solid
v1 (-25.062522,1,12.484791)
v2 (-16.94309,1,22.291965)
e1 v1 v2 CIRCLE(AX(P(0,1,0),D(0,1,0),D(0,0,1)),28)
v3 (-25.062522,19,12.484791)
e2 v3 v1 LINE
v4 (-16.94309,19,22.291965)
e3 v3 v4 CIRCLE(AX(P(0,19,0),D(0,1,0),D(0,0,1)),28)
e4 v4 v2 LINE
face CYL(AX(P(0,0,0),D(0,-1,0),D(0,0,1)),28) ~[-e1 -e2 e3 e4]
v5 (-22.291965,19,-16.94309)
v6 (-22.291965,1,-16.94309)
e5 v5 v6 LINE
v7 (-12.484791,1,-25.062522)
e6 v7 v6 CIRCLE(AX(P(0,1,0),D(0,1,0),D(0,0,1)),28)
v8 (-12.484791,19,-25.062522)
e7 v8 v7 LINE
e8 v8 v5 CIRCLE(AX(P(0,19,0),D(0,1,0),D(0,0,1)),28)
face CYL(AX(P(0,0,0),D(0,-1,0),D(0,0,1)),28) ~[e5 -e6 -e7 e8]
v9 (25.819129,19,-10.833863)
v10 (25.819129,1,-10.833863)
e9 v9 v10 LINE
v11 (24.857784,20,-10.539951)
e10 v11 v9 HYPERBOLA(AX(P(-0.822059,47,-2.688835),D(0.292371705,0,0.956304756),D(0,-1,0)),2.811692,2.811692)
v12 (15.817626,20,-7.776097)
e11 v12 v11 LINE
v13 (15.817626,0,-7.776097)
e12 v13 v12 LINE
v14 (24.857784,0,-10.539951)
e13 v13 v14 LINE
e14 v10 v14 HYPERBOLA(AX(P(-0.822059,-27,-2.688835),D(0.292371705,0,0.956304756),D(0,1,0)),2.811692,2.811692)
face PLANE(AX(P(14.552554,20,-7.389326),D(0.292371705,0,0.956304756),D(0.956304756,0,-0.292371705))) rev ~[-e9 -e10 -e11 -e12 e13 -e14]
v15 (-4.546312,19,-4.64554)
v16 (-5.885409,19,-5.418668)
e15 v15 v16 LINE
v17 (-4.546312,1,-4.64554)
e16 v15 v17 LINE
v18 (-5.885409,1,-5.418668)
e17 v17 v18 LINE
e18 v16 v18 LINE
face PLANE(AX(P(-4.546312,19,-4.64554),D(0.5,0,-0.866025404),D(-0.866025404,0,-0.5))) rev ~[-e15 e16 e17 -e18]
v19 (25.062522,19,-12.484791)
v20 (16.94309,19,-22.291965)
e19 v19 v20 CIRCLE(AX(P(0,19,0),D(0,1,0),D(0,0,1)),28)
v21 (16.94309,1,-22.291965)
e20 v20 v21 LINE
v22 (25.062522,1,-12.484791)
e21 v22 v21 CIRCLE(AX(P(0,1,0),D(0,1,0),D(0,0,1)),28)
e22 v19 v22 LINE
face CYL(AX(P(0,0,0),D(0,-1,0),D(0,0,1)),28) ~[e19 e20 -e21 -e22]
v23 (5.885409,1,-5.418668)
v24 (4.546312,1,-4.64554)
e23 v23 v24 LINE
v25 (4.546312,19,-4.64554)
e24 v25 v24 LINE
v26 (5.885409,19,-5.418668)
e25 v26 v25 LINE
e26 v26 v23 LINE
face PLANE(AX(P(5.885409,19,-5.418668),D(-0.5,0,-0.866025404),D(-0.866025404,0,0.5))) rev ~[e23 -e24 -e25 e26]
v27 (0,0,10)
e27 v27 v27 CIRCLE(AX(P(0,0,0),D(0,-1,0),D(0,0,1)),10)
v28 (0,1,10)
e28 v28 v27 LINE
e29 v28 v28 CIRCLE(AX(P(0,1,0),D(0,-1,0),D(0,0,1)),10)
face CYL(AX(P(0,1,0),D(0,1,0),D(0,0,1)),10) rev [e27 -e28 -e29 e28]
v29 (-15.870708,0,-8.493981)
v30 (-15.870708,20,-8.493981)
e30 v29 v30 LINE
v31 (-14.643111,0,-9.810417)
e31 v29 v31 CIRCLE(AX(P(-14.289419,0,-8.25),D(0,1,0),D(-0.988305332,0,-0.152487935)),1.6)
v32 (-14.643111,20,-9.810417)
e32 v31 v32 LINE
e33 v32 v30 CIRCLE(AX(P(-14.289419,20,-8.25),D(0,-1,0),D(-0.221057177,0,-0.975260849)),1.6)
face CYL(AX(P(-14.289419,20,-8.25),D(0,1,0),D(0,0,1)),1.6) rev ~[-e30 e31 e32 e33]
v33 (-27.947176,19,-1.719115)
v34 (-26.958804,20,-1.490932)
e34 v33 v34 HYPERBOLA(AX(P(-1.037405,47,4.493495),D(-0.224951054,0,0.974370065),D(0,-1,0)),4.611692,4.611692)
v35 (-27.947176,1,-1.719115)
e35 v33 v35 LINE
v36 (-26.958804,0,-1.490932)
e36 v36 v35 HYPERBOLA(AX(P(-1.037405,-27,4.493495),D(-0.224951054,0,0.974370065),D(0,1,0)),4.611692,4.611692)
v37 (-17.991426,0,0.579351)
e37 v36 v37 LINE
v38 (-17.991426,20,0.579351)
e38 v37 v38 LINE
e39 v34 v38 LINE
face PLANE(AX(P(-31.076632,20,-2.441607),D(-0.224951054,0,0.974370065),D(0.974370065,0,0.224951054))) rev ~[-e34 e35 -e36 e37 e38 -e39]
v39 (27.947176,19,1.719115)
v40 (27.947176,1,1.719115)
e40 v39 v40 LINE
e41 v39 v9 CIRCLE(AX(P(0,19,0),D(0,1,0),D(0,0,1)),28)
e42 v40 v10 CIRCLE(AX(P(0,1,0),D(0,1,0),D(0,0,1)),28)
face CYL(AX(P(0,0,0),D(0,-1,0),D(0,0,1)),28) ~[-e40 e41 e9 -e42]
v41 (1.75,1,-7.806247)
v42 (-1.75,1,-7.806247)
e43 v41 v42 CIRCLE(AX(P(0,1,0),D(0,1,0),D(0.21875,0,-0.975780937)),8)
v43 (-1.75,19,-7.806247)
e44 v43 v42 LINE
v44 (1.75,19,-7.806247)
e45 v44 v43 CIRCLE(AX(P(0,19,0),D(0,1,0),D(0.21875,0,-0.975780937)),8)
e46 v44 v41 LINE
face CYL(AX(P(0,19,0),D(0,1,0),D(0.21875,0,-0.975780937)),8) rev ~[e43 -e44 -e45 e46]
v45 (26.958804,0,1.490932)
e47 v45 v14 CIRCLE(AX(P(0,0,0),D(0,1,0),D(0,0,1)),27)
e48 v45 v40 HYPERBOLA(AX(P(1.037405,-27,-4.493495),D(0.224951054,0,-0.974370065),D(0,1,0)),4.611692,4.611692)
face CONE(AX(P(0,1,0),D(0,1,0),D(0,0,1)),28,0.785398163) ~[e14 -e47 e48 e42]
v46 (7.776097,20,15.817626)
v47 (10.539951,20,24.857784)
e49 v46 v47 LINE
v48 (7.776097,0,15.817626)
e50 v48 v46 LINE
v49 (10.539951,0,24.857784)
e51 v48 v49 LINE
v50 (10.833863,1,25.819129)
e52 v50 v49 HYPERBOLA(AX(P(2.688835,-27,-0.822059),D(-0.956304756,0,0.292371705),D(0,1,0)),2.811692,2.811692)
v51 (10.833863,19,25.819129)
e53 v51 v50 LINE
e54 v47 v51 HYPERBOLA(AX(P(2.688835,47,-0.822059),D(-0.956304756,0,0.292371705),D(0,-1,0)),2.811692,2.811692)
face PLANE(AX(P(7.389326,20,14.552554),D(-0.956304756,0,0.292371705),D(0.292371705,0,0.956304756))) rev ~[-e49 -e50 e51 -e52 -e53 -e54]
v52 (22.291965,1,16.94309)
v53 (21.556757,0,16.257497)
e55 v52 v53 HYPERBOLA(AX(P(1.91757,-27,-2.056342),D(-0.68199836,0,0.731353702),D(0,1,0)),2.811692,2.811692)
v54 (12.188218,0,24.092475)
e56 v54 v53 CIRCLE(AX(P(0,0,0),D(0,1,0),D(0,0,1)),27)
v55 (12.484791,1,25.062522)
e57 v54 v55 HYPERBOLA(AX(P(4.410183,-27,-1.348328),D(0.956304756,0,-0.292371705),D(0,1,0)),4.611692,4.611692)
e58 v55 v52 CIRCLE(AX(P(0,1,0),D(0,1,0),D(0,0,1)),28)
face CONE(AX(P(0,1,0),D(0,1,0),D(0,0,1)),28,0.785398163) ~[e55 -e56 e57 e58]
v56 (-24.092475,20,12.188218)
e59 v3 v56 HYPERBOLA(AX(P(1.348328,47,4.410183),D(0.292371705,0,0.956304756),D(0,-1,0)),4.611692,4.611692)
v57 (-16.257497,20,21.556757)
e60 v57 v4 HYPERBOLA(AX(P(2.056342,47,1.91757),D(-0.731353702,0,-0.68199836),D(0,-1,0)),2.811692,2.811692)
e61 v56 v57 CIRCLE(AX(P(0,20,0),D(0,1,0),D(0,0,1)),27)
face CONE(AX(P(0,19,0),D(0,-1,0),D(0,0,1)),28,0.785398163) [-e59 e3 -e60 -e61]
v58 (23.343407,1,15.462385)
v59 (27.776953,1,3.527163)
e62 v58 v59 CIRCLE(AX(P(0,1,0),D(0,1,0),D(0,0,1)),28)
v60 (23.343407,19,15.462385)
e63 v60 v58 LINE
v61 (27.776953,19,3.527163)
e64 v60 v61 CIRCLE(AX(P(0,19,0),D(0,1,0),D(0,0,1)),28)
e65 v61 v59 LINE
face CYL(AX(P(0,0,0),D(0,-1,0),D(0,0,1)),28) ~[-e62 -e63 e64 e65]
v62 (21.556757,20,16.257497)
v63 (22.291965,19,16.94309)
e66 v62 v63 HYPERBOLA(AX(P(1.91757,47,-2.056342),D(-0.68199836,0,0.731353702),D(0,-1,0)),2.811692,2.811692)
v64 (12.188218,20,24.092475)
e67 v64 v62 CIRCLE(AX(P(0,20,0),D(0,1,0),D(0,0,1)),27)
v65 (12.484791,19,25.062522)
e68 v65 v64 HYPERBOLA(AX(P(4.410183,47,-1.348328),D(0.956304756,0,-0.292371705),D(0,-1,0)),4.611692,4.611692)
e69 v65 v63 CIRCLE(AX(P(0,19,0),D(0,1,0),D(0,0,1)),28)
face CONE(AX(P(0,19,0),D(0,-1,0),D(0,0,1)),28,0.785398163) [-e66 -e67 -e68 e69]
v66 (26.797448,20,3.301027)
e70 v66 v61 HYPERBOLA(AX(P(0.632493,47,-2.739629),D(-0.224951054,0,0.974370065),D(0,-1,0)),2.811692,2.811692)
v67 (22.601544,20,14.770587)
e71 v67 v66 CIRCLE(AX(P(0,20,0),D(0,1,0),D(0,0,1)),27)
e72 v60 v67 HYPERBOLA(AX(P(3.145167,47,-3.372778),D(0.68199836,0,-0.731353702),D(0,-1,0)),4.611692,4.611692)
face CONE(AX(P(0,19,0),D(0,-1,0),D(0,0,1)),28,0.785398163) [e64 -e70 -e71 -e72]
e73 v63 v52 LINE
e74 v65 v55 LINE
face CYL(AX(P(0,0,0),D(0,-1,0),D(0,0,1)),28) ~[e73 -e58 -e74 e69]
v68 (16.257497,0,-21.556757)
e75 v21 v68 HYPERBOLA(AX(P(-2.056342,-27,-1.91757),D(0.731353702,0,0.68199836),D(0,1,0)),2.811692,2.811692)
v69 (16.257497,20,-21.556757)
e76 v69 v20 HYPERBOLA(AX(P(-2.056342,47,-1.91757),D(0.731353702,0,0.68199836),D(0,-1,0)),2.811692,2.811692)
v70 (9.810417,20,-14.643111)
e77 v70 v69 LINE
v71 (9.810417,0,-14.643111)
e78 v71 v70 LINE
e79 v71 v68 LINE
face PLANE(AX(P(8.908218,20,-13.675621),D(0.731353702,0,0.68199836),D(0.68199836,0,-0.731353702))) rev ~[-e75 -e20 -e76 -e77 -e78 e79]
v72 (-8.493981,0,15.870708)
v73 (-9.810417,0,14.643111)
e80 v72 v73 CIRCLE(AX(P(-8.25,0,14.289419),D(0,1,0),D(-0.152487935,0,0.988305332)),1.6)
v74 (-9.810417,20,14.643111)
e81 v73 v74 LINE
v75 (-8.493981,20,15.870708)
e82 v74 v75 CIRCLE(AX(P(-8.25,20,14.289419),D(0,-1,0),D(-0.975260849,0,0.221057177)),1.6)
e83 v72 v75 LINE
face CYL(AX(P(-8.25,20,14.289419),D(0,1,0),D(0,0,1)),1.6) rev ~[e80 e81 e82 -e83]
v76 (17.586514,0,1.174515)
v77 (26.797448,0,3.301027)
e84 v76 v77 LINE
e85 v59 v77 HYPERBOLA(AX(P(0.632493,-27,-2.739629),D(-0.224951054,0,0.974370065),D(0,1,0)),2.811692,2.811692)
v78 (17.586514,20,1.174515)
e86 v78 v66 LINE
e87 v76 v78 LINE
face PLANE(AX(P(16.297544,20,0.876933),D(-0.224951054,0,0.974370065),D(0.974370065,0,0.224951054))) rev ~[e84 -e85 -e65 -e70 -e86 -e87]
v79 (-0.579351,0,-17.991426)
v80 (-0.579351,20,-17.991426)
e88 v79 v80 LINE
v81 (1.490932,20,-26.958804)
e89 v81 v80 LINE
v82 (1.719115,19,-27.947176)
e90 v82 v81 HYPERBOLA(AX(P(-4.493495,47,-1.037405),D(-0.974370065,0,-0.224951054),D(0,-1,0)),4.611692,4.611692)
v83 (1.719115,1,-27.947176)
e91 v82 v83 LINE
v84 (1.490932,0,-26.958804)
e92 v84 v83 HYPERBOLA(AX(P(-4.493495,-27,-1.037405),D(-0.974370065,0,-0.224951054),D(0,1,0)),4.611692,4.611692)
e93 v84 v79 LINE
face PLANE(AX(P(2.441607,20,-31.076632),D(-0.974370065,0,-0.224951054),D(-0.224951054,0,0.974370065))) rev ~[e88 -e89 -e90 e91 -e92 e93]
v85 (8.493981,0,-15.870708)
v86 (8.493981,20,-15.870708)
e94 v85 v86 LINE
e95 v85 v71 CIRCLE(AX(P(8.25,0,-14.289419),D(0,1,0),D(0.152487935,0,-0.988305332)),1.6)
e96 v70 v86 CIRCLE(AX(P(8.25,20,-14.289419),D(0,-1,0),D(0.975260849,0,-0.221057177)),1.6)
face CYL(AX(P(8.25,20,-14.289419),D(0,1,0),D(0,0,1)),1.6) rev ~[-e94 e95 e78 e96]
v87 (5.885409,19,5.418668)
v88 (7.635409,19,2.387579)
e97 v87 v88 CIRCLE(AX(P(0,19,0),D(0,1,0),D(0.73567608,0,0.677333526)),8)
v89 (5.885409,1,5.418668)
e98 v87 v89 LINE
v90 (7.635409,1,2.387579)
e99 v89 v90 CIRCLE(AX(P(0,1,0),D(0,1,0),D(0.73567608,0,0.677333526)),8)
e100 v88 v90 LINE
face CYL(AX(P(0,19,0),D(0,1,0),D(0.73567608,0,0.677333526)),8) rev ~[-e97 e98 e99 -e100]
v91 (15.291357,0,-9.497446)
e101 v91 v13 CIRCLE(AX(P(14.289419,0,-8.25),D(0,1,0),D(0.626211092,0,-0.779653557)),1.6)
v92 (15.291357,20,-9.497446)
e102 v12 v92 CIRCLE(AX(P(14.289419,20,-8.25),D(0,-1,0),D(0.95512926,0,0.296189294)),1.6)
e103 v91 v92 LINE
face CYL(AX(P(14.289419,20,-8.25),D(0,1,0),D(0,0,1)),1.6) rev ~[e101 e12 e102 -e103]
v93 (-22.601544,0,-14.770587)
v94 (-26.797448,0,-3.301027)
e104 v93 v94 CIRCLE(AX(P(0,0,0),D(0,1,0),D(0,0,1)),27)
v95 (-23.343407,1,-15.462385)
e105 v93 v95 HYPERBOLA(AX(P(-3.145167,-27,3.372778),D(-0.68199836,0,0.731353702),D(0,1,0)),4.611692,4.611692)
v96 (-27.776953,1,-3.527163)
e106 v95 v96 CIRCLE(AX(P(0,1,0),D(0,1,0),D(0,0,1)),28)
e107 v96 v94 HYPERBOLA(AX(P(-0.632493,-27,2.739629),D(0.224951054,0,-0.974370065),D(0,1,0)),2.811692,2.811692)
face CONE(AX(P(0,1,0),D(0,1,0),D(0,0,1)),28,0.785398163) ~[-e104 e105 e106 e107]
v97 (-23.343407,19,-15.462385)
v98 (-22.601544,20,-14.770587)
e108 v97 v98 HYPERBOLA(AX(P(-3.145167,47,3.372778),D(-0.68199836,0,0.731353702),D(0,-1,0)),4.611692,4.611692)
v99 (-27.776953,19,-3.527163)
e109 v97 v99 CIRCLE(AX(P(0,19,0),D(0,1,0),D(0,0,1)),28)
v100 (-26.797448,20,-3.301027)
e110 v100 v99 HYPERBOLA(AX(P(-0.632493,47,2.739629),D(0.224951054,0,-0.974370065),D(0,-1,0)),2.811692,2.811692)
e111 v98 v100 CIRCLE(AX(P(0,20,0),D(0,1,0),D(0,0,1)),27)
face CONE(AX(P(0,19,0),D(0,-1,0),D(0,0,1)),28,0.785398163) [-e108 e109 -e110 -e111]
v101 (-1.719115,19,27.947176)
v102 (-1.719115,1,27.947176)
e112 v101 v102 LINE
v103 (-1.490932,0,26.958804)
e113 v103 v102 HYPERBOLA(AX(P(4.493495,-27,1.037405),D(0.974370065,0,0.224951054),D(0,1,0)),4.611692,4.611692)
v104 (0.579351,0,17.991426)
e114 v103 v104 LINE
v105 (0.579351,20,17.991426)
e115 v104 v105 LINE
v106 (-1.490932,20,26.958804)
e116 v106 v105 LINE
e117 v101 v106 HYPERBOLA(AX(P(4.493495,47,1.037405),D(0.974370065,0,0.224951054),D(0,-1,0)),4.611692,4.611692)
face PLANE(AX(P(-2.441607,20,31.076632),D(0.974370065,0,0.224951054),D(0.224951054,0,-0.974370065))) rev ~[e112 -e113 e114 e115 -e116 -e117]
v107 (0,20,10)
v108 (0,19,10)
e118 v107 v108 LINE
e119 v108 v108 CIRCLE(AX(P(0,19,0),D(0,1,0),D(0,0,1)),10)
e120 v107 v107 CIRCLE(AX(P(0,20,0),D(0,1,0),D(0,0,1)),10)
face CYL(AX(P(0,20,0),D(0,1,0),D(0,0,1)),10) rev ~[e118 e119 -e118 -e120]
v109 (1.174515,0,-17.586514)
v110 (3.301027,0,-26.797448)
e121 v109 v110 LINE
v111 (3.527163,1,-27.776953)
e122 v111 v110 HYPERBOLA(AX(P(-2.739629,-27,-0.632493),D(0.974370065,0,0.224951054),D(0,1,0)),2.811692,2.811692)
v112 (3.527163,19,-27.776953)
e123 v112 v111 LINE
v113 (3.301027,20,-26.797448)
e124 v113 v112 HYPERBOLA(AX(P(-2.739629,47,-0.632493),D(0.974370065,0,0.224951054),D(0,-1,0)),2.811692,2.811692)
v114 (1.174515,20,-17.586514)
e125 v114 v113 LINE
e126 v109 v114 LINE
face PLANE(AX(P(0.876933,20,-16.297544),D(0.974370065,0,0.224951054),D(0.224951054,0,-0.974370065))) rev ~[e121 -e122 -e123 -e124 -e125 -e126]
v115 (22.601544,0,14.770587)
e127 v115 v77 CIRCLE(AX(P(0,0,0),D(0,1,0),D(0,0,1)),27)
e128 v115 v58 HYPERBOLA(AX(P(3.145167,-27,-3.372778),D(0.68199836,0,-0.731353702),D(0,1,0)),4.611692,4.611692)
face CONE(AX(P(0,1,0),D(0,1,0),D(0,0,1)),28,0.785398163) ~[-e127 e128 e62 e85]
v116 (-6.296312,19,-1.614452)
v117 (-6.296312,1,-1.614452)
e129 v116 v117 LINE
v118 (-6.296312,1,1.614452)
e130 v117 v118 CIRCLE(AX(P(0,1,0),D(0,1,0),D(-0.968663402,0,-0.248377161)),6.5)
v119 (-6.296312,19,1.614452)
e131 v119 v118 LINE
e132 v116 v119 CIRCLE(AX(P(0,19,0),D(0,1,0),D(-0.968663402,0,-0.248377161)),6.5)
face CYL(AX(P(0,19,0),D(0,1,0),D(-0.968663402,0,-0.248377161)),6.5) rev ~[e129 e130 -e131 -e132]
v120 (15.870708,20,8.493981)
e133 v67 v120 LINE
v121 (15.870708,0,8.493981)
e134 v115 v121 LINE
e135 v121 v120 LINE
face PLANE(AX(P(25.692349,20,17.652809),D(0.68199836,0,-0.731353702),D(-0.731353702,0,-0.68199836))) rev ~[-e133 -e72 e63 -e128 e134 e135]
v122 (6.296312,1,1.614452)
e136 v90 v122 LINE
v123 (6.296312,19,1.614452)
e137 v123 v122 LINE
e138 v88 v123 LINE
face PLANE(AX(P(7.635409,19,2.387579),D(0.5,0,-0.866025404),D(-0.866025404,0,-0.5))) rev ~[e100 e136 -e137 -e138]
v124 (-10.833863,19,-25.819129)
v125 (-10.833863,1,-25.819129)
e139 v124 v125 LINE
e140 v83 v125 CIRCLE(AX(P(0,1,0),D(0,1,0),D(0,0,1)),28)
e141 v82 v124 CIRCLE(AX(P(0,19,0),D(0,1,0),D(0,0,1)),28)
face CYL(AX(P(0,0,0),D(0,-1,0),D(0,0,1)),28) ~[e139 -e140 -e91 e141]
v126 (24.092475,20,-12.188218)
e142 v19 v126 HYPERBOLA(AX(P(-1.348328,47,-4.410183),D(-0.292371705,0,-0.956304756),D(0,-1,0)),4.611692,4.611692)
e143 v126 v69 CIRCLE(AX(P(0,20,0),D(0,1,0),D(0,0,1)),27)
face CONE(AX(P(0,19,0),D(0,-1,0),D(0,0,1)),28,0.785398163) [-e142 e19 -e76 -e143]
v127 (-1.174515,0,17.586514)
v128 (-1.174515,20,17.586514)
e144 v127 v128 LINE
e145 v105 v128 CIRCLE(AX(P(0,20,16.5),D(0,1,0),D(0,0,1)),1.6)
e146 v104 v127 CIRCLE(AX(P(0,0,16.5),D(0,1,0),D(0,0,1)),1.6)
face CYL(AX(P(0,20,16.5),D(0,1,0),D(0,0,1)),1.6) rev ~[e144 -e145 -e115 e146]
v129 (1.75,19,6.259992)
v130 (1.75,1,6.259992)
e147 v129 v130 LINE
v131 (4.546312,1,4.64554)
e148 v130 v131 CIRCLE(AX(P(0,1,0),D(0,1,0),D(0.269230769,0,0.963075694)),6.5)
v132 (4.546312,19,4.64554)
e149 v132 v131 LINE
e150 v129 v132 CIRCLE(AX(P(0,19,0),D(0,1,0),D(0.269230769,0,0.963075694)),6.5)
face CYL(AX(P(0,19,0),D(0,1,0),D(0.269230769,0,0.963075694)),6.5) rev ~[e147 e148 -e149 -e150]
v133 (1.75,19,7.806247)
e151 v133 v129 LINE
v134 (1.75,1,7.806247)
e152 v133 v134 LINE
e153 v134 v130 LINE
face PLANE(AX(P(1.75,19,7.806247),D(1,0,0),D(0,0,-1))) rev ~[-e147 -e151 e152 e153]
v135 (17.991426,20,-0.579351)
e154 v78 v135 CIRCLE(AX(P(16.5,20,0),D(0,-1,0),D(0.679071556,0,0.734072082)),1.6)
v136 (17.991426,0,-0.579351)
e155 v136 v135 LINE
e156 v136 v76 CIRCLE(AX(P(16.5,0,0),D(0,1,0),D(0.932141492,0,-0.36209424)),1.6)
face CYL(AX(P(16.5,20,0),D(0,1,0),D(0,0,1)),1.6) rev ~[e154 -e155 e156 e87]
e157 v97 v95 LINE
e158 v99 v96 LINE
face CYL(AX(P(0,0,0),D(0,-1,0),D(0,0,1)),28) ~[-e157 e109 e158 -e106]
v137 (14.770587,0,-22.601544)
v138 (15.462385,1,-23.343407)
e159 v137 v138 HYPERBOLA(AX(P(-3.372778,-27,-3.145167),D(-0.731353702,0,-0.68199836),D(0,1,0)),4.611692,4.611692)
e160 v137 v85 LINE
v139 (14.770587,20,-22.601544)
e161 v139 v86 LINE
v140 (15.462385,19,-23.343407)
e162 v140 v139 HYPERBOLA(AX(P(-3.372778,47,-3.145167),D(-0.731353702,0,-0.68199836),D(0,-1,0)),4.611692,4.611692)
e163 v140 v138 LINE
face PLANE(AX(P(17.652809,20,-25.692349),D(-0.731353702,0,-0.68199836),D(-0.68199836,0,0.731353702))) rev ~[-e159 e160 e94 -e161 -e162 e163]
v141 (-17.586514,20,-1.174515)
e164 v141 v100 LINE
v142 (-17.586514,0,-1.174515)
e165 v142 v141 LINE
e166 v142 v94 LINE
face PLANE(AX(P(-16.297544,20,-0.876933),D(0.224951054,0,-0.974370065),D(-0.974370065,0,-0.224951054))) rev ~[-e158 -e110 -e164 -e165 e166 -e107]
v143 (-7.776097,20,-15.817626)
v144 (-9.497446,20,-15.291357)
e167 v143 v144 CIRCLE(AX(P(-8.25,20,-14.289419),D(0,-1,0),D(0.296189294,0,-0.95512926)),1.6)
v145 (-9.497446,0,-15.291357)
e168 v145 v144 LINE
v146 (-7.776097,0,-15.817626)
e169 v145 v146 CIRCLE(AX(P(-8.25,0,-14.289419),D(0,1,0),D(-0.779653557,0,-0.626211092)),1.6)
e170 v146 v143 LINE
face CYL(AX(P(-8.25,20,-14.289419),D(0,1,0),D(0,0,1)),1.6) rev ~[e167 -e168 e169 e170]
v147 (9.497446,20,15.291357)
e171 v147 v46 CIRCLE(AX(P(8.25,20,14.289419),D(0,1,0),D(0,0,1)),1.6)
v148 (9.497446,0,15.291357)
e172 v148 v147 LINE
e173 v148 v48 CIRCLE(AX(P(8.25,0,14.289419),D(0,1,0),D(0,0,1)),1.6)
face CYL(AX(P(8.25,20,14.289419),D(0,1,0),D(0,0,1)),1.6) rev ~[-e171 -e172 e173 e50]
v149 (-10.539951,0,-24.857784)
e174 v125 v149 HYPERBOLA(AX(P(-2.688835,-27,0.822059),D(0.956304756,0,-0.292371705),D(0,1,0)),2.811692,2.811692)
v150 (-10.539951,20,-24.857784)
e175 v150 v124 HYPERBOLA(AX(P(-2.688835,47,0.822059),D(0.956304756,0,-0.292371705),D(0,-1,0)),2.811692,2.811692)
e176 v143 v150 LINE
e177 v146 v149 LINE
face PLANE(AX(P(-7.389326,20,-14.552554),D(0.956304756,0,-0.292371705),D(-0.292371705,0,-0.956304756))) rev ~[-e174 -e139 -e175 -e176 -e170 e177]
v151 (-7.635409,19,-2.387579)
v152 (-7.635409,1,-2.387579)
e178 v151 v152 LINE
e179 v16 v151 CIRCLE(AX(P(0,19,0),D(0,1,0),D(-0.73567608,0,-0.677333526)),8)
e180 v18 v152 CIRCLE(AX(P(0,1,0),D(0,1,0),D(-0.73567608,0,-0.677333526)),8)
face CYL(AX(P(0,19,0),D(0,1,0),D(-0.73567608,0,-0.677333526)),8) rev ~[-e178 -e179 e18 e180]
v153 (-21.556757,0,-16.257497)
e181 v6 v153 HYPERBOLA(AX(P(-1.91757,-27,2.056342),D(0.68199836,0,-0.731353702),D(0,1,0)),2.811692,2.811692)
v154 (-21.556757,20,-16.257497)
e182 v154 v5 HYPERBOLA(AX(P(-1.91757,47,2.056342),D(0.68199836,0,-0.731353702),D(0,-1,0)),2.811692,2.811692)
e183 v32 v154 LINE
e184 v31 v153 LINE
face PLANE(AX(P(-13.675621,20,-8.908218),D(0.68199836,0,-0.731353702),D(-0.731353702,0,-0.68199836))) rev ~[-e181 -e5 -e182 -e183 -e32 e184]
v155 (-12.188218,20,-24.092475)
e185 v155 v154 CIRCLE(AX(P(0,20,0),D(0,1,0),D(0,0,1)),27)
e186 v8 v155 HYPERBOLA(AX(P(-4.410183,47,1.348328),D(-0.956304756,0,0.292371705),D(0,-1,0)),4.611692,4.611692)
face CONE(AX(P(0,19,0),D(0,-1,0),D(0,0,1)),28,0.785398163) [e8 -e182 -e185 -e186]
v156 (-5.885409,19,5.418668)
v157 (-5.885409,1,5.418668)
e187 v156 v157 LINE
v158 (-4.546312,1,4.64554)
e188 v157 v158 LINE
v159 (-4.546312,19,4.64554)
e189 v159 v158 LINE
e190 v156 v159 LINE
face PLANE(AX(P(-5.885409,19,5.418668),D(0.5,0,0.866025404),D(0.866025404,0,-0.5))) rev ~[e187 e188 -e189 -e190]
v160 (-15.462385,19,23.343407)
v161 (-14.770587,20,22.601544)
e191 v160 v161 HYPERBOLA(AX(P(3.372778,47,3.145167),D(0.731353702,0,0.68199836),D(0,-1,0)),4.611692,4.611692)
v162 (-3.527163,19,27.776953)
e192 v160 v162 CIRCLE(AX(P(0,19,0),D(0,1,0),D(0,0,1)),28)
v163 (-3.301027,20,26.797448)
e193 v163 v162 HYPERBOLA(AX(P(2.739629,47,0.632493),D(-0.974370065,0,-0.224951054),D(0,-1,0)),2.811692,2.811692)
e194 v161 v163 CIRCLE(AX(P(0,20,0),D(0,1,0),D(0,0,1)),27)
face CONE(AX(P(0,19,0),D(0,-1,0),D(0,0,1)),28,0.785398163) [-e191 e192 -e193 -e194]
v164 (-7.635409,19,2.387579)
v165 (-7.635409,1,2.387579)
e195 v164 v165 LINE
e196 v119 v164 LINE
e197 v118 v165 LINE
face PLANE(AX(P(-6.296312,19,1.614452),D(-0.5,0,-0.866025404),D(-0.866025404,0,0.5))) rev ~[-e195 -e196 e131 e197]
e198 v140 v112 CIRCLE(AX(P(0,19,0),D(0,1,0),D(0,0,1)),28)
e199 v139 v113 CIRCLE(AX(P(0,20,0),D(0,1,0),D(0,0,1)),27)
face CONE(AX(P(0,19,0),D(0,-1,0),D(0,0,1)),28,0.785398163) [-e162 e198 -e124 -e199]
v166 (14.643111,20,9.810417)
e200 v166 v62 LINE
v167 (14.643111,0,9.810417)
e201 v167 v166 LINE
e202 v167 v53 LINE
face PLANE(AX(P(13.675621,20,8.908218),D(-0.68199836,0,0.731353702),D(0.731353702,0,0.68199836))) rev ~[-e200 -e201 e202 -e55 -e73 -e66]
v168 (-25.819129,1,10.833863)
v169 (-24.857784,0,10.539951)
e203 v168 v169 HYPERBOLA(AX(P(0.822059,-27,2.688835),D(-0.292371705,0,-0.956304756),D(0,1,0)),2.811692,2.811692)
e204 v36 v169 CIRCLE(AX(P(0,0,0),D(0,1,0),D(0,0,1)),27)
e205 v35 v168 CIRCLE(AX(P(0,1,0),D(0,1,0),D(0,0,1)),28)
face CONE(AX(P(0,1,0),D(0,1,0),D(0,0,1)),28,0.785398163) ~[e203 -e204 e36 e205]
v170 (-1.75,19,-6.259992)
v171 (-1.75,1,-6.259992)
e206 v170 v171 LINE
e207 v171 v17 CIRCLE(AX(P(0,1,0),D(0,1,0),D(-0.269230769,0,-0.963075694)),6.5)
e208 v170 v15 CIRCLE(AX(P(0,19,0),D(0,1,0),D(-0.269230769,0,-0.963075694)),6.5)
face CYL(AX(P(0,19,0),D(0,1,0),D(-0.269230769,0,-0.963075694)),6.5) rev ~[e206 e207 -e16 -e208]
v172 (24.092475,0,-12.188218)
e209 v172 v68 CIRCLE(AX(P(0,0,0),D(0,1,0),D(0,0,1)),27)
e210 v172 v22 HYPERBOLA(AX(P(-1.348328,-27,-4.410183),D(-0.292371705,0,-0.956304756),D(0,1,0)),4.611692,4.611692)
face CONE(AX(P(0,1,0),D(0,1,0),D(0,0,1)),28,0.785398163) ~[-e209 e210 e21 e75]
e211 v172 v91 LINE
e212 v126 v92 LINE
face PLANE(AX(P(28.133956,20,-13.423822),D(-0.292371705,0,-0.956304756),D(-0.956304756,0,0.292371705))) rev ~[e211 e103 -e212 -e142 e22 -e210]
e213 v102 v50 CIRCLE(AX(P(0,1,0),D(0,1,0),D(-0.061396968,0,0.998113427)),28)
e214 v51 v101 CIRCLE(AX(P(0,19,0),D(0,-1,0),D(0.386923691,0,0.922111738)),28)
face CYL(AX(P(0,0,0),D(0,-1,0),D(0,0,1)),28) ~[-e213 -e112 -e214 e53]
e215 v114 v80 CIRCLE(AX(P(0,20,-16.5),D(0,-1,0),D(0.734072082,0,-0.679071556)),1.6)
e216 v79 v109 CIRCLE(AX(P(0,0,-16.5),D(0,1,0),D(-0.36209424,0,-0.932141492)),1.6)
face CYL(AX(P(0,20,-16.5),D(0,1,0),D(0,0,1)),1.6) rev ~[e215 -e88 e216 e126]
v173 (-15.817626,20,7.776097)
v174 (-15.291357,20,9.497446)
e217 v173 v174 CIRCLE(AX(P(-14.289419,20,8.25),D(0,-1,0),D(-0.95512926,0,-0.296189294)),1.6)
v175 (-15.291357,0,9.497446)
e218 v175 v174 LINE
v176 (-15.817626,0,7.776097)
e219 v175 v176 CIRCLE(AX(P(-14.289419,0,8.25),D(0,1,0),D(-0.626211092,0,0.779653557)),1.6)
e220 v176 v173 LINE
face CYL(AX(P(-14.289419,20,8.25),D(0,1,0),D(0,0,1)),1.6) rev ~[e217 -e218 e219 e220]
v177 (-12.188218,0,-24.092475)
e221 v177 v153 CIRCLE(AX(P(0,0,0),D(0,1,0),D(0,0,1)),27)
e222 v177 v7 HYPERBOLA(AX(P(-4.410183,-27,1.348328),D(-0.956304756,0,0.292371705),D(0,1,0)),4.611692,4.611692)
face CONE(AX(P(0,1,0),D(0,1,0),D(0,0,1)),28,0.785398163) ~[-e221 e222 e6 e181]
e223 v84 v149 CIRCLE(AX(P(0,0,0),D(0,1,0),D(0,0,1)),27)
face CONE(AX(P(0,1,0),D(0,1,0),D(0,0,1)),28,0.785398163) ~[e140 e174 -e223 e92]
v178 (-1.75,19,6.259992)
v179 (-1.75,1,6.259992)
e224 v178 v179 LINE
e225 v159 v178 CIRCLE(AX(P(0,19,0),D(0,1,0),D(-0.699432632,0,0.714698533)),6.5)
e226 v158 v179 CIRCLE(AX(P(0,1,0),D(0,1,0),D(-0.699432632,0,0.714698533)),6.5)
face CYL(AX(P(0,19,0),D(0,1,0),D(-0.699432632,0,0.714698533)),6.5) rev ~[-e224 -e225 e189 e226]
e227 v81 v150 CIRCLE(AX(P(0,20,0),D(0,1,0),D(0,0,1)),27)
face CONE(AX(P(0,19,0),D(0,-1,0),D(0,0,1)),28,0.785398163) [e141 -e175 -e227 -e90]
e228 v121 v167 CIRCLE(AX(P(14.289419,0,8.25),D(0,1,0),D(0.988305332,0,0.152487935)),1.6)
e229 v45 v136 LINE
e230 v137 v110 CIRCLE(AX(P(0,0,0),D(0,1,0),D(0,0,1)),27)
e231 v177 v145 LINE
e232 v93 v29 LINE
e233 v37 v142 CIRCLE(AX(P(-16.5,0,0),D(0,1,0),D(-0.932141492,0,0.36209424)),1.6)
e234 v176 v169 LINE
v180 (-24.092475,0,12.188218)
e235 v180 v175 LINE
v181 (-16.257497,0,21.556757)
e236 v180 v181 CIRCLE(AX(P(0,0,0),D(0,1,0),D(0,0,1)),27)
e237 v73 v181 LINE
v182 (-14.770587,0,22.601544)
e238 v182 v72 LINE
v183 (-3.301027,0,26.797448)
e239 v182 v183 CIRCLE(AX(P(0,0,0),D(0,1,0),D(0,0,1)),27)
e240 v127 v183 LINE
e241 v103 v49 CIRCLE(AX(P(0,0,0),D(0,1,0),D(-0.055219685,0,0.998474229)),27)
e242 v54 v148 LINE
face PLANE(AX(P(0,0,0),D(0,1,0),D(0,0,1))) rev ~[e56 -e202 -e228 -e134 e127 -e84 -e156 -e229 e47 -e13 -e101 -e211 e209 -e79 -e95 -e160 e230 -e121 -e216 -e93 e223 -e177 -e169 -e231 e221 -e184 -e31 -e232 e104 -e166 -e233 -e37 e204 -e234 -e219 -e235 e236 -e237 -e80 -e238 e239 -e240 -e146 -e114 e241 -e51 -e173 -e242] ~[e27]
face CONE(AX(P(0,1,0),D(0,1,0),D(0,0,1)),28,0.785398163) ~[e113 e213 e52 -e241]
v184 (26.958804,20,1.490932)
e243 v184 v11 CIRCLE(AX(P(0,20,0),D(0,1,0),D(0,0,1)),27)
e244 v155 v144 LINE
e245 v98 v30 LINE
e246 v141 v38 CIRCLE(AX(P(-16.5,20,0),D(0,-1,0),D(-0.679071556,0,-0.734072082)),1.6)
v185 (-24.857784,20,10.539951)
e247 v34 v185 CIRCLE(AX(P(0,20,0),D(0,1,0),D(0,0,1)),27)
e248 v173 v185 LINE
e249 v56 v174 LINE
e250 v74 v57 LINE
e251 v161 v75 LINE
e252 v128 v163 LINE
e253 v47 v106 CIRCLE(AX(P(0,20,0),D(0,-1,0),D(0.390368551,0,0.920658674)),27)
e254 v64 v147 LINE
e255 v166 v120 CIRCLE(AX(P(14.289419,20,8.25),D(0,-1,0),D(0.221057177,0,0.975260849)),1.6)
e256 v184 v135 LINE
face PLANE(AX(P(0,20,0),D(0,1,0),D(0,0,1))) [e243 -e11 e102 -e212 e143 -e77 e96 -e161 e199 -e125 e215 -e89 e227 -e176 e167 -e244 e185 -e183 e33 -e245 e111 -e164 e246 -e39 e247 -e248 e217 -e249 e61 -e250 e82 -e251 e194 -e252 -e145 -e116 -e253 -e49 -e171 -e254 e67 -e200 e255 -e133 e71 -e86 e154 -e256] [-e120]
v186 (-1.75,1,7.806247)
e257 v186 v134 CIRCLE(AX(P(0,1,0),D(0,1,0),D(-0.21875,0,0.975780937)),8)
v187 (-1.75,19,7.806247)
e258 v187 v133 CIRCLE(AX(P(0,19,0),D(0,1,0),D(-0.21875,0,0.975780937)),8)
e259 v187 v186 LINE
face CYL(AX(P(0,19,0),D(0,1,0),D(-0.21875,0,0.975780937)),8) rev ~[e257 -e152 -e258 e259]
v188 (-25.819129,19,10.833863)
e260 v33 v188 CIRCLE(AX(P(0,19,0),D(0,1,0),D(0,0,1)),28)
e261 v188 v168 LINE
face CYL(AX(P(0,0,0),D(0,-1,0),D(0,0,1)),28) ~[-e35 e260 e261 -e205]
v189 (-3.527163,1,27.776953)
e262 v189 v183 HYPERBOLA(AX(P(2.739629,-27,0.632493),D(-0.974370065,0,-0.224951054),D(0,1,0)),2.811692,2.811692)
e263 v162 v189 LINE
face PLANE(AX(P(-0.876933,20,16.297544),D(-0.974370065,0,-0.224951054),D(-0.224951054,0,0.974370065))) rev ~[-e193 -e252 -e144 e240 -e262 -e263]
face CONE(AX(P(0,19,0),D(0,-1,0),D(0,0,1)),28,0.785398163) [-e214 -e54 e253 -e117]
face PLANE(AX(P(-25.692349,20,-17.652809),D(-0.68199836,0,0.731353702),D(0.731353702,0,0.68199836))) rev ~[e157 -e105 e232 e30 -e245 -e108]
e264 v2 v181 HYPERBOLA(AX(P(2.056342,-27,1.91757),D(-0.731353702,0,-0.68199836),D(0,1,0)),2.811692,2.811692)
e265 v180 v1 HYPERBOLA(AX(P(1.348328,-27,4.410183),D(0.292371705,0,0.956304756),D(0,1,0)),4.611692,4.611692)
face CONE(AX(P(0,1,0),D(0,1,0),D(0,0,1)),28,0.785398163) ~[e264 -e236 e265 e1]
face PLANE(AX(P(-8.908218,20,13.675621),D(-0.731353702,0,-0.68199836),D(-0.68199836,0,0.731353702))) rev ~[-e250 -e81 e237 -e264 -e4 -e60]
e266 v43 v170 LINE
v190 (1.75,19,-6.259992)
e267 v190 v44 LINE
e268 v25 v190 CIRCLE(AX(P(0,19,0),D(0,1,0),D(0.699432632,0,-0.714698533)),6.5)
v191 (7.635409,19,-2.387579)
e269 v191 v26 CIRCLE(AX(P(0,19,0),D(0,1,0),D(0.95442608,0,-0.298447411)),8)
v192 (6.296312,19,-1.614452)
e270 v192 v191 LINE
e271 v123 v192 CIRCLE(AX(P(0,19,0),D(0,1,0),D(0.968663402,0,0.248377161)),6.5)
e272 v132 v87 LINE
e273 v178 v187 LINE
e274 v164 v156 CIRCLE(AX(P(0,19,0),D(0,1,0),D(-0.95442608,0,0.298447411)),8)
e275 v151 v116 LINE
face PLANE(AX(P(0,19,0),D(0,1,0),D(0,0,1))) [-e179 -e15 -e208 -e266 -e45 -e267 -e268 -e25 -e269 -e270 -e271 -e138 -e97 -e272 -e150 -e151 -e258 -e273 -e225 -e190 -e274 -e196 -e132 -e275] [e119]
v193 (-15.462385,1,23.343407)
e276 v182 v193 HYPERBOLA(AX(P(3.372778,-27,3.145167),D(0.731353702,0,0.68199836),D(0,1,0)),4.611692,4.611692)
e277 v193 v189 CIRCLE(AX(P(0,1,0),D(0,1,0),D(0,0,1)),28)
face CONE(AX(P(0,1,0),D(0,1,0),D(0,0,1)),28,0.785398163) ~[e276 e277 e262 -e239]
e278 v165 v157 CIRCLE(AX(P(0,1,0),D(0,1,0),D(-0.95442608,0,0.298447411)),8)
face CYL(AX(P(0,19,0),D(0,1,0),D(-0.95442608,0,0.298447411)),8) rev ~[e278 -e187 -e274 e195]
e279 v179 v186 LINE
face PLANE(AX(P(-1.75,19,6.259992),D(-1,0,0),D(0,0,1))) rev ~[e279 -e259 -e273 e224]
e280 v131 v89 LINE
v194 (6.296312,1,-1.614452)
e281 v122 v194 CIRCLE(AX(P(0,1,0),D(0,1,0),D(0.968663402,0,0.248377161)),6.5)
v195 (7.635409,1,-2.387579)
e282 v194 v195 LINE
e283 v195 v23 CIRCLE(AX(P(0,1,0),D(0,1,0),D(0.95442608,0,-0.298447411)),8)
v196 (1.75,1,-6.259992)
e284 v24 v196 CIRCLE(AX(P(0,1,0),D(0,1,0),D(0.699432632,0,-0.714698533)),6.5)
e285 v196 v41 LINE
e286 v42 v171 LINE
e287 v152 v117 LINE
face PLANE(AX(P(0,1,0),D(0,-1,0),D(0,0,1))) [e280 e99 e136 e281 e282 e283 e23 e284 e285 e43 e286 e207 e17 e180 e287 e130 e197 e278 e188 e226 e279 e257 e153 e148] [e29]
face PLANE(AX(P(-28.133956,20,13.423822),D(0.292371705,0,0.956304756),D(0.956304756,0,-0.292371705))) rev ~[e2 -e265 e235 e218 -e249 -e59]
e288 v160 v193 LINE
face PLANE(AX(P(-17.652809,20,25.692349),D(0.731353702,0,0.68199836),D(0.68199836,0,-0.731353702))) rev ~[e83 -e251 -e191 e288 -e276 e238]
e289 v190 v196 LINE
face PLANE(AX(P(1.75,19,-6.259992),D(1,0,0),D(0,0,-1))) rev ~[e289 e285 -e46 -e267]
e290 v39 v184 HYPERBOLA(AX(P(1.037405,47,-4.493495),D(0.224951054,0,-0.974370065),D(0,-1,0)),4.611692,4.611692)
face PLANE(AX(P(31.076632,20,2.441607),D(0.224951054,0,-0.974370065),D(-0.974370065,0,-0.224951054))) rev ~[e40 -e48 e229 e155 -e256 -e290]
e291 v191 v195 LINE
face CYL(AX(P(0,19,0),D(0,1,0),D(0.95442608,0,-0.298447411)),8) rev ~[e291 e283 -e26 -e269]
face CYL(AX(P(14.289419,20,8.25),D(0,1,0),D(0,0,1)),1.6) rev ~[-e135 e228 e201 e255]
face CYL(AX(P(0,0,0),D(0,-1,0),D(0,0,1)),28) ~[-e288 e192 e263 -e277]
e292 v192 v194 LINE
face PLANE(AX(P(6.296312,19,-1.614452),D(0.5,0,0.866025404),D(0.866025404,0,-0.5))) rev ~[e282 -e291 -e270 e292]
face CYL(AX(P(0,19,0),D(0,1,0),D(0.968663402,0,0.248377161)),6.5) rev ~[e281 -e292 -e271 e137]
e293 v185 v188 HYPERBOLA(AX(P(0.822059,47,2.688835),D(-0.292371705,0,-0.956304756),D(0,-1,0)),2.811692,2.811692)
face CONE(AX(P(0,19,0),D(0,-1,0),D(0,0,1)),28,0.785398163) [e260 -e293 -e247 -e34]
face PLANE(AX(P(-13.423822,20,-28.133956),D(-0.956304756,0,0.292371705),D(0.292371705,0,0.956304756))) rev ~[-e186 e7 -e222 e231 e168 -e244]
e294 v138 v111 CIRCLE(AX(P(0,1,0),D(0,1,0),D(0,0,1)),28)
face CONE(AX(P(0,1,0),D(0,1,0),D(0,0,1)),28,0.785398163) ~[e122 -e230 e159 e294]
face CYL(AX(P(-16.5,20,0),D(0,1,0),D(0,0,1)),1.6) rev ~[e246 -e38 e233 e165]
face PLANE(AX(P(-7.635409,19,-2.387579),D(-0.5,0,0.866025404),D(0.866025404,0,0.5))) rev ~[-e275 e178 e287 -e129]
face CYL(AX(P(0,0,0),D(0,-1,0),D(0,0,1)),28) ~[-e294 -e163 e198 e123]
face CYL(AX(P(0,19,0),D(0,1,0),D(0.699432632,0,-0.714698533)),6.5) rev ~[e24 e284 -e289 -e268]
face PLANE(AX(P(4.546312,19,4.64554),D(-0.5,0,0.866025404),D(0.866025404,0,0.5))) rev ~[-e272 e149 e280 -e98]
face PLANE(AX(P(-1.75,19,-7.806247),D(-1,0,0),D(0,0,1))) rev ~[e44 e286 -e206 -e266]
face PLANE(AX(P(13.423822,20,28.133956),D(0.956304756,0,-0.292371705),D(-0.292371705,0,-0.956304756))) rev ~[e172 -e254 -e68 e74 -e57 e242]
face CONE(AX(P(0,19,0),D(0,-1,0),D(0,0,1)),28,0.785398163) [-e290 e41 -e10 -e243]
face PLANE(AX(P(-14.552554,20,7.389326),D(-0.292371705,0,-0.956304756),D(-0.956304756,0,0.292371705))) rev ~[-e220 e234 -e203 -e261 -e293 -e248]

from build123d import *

# Parameters (mm, degrees)
SKETCH1_R           = 28
BOSS_EXTRUDE1_DEPTH = 20
SKETCH2_R           = 10
CUT_EXTRUDE1_DEPTH  = 1
CUT_EXTRUDE2_DEPTH  = 30
CUT_EXTRUDE3_START  = -1
SKETCH4_R           = 10
CUT_EXTRUDE3_DEPTH  = 1
SKETCH5_R           = 1.6
CUT_EXTRUDE4_DEPTH  = 80
CHAMFER1_SIZE       = 1
CUT_EXTRUDE5_DEPTH  = 80


with BuildPart() as part:
    # Sketch1 → Boss-Extrude1 (new body)
    with BuildSketch(Plane(origin=(0, 0, 0), x_dir=(1, 0, 0), z_dir=(0, 1, 0))):
        with Locations(Location((0, 0, 0), (0, 0, 270))):
            Circle(SKETCH1_R)
    extrude(amount=BOSS_EXTRUDE1_DEPTH)

    # Sketch2 → Cut-Extrude1 (cut)
    with BuildSketch(Plane(origin=(0, 20, 0), x_dir=(1, 0, 0), z_dir=(0, 1, 0))):
        with Locations(Location((0, 0, 0), (0, 0, 270))):
            Circle(SKETCH2_R)
    extrude(amount=-CUT_EXTRUDE1_DEPTH, mode=Mode.SUBTRACT)

    # Sketch3 → Cut-Extrude2 (cut)
    with BuildSketch(Plane(origin=(0, 19, 0), x_dir=(1, 0, 0), z_dir=(0, 1, 0))):
        with BuildLine():
            Line((-1.75, 7.806247498), (-1.75, 6.259992013))
            ThreePointArc((-1.75, 6.259992013), (-3.25, 5.629165125), (-4.546312111, 4.645540463))
            Line((-4.546312111, 4.645540463), (-5.885408641, 5.418668206))
            ThreePointArc((-5.885408641, 5.418668206), (-6.92820323, 4), (-7.635408641, 2.387579292))
            Line((-7.635408641, 2.387579292), (-6.296312111, 1.61445155))
            ThreePointArc((-6.296312111, 1.61445155), (-6.5, 0), (-6.296312111, -1.61445155))
            Line((-6.296312111, -1.61445155), (-7.635408641, -2.387579292))
            ThreePointArc((-7.635408641, -2.387579292), (-6.92820323, -4), (-5.885408641, -5.418668206))
            Line((-5.885408641, -5.418668206), (-4.546312111, -4.645540463))
            ThreePointArc((-4.546312111, -4.645540463), (-3.25, -5.629165125), (-1.75, -6.259992013))
            Line((-1.75, -6.259992013), (-1.75, -7.806247498))
            ThreePointArc((-1.75, -7.806247498), (0, -8), (1.75, -7.806247498))
            Line((1.75, -7.806247498), (1.75, -6.259992013))
            ThreePointArc((1.75, -6.259992013), (3.25, -5.629165125), (4.546312111, -4.645540463))
            Line((4.546312111, -4.645540463), (5.885408641, -5.418668206))
            ThreePointArc((5.885408641, -5.418668206), (6.92820323, -4), (7.635408641, -2.387579292))
            Line((7.635408641, -2.387579292), (6.296312111, -1.61445155))
            ThreePointArc((6.296312111, -1.61445155), (6.5, 0), (6.296312111, 1.61445155))
            Line((6.296312111, 1.61445155), (7.635408641, 2.387579292))
            ThreePointArc((7.635408641, 2.387579292), (6.92820323, 4), (5.885408641, 5.418668206))
            Line((5.885408641, 5.418668206), (4.546312111, 4.645540463))
            ThreePointArc((4.546312111, 4.645540463), (3.25, 5.629165125), (1.75, 6.259992013))
            Line((1.75, 6.259992013), (1.75, 7.806247498))
            ThreePointArc((1.75, 7.806247498), (0, 8), (-1.75, 7.806247498))
        make_face()
    extrude(amount=-CUT_EXTRUDE2_DEPTH, mode=Mode.SUBTRACT)

    # Sketch4 → Cut-Extrude3 (cut)
    with BuildSketch(Plane(origin=(0, 0, 0), x_dir=(-1, 0, 0), z_dir=(0, -1, 0)).offset(CUT_EXTRUDE3_START)):
        with Locations(Location((0, 0, 0), (0, 0, 270))):
            Circle(SKETCH4_R)
    extrude(amount=CUT_EXTRUDE3_DEPTH, mode=Mode.SUBTRACT)

    # Sketch5 → Cut-Extrude4 (cut)
    with BuildSketch(Plane(origin=(0, 20, 0), x_dir=(1, 0, 0), z_dir=(0, 1, 0))):
        with Locations(Location((0, 16.5, 0), (0, 0, 270))):
            Circle(SKETCH5_R)
        with Locations(Location((8.25, 14.289419162, 0), (0, 0, 270))):
            Circle(SKETCH5_R)
        with Locations(Location((14.289419162, 8.25, 0), (0, 0, 270))):
            Circle(SKETCH5_R)
        with Locations(Location((16.5, 0, 0), (0, 0, 270))):
            Circle(SKETCH5_R)
        with Locations(Location((14.289419162, -8.25, 0), (0, 0, 270))):
            Circle(SKETCH5_R)
        with Locations(Location((8.25, -14.289419162, 0), (0, 0, 270))):
            Circle(SKETCH5_R)
        with Locations(Location((0, -16.5, 0), (0, 0, 270))):
            Circle(SKETCH5_R)
        with Locations(Location((-8.25, -14.289419162, 0), (0, 0, 270))):
            Circle(SKETCH5_R)
        with Locations(Location((-14.289419162, -8.25, 0), (0, 0, 270))):
            Circle(SKETCH5_R)
        with Locations(Location((-16.5, 0, 0), (0, 0, 270))):
            Circle(SKETCH5_R)
        with Locations(Location((-14.289419162, 8.25, 0), (0, 0, 270))):
            Circle(SKETCH5_R)
        with Locations(Location((-8.25, 14.289419162, 0), (0, 0, 270))):
            Circle(SKETCH5_R)
    extrude(amount=-CUT_EXTRUDE4_DEPTH, mode=Mode.SUBTRACT)

    # Chamfer1
    chamfer1_edges = [part.edges().sort_by_distance(p)[0] for p in [
        (0, 0, -28),
        (0, 20, -28),
    ]]
    chamfer(chamfer1_edges, length=CHAMFER1_SIZE)

    # Sketch6 → Cut-Extrude5 (cut)
    with BuildSketch(Plane(origin=(0, 20, 0), x_dir=(1, 0, 0), z_dir=(0, 1, 0))):
        Polygon((0.876933058, 16.297544051), (4.195472987, 30.671719689), (2.44160687, 31.076631587), (-0.876933058, 16.702455949), align=None)
        Polygon((7.591781669, 14.903217686), (8.908218331, 13.675620638), (18.969246032, 24.464751935), (17.652809369, 25.692348984), align=None)
        Polygon((14.026284628, 9.11067428), (14.552553697, 7.38932572), (28.660224922, 11.702473657), (28.133955854, 13.423822218), align=None)
        Polygon((16.702455949, 0.876933058), (16.297544051, -0.876933058), (30.671719689, -4.195472987), (31.076631587, -2.44160687), align=None)
        Polygon((14.903217687, -7.591781669), (13.675620638, -8.908218331), (24.464751935, -18.969246032), (25.692348984, -17.652809369), align=None)
        Polygon((9.11067428, -14.026284628), (7.38932572, -14.552553697), (11.702473657, -28.660224922), (13.423822218, -28.133955854), align=None)
        Polygon((0.876933058, -16.702455949), (-0.876933058, -16.297544051), (-4.195472987, -30.671719689), (-2.44160687, -31.076631587), align=None)
        Polygon((-7.591781669, -14.903217686), (-8.908218331, -13.675620638), (-18.969246032, -24.464751935), (-17.652809369, -25.692348984), align=None)
        Polygon((-14.026284628, -9.11067428), (-14.552553697, -7.38932572), (-28.660224922, -11.702473657), (-28.133955854, -13.423822218), align=None)
        Polygon((-16.702455949, -0.876933058), (-16.297544051, 0.876933058), (-30.671719689, 4.195472987), (-31.076631587, 2.44160687), align=None)
        Polygon((-14.903217686, 7.591781669), (-13.675620638, 8.908218331), (-24.464751935, 18.969246032), (-25.692348984, 17.652809369), align=None)
        Polygon((-9.11067428, 14.026284628), (-7.38932572, 14.552553697), (-11.702473657, 28.660224922), (-13.423822218, 28.133955854), align=None)
    extrude(amount=-CUT_EXTRUDE5_DEPTH, mode=Mode.SUBTRACT)


solid = part.part
